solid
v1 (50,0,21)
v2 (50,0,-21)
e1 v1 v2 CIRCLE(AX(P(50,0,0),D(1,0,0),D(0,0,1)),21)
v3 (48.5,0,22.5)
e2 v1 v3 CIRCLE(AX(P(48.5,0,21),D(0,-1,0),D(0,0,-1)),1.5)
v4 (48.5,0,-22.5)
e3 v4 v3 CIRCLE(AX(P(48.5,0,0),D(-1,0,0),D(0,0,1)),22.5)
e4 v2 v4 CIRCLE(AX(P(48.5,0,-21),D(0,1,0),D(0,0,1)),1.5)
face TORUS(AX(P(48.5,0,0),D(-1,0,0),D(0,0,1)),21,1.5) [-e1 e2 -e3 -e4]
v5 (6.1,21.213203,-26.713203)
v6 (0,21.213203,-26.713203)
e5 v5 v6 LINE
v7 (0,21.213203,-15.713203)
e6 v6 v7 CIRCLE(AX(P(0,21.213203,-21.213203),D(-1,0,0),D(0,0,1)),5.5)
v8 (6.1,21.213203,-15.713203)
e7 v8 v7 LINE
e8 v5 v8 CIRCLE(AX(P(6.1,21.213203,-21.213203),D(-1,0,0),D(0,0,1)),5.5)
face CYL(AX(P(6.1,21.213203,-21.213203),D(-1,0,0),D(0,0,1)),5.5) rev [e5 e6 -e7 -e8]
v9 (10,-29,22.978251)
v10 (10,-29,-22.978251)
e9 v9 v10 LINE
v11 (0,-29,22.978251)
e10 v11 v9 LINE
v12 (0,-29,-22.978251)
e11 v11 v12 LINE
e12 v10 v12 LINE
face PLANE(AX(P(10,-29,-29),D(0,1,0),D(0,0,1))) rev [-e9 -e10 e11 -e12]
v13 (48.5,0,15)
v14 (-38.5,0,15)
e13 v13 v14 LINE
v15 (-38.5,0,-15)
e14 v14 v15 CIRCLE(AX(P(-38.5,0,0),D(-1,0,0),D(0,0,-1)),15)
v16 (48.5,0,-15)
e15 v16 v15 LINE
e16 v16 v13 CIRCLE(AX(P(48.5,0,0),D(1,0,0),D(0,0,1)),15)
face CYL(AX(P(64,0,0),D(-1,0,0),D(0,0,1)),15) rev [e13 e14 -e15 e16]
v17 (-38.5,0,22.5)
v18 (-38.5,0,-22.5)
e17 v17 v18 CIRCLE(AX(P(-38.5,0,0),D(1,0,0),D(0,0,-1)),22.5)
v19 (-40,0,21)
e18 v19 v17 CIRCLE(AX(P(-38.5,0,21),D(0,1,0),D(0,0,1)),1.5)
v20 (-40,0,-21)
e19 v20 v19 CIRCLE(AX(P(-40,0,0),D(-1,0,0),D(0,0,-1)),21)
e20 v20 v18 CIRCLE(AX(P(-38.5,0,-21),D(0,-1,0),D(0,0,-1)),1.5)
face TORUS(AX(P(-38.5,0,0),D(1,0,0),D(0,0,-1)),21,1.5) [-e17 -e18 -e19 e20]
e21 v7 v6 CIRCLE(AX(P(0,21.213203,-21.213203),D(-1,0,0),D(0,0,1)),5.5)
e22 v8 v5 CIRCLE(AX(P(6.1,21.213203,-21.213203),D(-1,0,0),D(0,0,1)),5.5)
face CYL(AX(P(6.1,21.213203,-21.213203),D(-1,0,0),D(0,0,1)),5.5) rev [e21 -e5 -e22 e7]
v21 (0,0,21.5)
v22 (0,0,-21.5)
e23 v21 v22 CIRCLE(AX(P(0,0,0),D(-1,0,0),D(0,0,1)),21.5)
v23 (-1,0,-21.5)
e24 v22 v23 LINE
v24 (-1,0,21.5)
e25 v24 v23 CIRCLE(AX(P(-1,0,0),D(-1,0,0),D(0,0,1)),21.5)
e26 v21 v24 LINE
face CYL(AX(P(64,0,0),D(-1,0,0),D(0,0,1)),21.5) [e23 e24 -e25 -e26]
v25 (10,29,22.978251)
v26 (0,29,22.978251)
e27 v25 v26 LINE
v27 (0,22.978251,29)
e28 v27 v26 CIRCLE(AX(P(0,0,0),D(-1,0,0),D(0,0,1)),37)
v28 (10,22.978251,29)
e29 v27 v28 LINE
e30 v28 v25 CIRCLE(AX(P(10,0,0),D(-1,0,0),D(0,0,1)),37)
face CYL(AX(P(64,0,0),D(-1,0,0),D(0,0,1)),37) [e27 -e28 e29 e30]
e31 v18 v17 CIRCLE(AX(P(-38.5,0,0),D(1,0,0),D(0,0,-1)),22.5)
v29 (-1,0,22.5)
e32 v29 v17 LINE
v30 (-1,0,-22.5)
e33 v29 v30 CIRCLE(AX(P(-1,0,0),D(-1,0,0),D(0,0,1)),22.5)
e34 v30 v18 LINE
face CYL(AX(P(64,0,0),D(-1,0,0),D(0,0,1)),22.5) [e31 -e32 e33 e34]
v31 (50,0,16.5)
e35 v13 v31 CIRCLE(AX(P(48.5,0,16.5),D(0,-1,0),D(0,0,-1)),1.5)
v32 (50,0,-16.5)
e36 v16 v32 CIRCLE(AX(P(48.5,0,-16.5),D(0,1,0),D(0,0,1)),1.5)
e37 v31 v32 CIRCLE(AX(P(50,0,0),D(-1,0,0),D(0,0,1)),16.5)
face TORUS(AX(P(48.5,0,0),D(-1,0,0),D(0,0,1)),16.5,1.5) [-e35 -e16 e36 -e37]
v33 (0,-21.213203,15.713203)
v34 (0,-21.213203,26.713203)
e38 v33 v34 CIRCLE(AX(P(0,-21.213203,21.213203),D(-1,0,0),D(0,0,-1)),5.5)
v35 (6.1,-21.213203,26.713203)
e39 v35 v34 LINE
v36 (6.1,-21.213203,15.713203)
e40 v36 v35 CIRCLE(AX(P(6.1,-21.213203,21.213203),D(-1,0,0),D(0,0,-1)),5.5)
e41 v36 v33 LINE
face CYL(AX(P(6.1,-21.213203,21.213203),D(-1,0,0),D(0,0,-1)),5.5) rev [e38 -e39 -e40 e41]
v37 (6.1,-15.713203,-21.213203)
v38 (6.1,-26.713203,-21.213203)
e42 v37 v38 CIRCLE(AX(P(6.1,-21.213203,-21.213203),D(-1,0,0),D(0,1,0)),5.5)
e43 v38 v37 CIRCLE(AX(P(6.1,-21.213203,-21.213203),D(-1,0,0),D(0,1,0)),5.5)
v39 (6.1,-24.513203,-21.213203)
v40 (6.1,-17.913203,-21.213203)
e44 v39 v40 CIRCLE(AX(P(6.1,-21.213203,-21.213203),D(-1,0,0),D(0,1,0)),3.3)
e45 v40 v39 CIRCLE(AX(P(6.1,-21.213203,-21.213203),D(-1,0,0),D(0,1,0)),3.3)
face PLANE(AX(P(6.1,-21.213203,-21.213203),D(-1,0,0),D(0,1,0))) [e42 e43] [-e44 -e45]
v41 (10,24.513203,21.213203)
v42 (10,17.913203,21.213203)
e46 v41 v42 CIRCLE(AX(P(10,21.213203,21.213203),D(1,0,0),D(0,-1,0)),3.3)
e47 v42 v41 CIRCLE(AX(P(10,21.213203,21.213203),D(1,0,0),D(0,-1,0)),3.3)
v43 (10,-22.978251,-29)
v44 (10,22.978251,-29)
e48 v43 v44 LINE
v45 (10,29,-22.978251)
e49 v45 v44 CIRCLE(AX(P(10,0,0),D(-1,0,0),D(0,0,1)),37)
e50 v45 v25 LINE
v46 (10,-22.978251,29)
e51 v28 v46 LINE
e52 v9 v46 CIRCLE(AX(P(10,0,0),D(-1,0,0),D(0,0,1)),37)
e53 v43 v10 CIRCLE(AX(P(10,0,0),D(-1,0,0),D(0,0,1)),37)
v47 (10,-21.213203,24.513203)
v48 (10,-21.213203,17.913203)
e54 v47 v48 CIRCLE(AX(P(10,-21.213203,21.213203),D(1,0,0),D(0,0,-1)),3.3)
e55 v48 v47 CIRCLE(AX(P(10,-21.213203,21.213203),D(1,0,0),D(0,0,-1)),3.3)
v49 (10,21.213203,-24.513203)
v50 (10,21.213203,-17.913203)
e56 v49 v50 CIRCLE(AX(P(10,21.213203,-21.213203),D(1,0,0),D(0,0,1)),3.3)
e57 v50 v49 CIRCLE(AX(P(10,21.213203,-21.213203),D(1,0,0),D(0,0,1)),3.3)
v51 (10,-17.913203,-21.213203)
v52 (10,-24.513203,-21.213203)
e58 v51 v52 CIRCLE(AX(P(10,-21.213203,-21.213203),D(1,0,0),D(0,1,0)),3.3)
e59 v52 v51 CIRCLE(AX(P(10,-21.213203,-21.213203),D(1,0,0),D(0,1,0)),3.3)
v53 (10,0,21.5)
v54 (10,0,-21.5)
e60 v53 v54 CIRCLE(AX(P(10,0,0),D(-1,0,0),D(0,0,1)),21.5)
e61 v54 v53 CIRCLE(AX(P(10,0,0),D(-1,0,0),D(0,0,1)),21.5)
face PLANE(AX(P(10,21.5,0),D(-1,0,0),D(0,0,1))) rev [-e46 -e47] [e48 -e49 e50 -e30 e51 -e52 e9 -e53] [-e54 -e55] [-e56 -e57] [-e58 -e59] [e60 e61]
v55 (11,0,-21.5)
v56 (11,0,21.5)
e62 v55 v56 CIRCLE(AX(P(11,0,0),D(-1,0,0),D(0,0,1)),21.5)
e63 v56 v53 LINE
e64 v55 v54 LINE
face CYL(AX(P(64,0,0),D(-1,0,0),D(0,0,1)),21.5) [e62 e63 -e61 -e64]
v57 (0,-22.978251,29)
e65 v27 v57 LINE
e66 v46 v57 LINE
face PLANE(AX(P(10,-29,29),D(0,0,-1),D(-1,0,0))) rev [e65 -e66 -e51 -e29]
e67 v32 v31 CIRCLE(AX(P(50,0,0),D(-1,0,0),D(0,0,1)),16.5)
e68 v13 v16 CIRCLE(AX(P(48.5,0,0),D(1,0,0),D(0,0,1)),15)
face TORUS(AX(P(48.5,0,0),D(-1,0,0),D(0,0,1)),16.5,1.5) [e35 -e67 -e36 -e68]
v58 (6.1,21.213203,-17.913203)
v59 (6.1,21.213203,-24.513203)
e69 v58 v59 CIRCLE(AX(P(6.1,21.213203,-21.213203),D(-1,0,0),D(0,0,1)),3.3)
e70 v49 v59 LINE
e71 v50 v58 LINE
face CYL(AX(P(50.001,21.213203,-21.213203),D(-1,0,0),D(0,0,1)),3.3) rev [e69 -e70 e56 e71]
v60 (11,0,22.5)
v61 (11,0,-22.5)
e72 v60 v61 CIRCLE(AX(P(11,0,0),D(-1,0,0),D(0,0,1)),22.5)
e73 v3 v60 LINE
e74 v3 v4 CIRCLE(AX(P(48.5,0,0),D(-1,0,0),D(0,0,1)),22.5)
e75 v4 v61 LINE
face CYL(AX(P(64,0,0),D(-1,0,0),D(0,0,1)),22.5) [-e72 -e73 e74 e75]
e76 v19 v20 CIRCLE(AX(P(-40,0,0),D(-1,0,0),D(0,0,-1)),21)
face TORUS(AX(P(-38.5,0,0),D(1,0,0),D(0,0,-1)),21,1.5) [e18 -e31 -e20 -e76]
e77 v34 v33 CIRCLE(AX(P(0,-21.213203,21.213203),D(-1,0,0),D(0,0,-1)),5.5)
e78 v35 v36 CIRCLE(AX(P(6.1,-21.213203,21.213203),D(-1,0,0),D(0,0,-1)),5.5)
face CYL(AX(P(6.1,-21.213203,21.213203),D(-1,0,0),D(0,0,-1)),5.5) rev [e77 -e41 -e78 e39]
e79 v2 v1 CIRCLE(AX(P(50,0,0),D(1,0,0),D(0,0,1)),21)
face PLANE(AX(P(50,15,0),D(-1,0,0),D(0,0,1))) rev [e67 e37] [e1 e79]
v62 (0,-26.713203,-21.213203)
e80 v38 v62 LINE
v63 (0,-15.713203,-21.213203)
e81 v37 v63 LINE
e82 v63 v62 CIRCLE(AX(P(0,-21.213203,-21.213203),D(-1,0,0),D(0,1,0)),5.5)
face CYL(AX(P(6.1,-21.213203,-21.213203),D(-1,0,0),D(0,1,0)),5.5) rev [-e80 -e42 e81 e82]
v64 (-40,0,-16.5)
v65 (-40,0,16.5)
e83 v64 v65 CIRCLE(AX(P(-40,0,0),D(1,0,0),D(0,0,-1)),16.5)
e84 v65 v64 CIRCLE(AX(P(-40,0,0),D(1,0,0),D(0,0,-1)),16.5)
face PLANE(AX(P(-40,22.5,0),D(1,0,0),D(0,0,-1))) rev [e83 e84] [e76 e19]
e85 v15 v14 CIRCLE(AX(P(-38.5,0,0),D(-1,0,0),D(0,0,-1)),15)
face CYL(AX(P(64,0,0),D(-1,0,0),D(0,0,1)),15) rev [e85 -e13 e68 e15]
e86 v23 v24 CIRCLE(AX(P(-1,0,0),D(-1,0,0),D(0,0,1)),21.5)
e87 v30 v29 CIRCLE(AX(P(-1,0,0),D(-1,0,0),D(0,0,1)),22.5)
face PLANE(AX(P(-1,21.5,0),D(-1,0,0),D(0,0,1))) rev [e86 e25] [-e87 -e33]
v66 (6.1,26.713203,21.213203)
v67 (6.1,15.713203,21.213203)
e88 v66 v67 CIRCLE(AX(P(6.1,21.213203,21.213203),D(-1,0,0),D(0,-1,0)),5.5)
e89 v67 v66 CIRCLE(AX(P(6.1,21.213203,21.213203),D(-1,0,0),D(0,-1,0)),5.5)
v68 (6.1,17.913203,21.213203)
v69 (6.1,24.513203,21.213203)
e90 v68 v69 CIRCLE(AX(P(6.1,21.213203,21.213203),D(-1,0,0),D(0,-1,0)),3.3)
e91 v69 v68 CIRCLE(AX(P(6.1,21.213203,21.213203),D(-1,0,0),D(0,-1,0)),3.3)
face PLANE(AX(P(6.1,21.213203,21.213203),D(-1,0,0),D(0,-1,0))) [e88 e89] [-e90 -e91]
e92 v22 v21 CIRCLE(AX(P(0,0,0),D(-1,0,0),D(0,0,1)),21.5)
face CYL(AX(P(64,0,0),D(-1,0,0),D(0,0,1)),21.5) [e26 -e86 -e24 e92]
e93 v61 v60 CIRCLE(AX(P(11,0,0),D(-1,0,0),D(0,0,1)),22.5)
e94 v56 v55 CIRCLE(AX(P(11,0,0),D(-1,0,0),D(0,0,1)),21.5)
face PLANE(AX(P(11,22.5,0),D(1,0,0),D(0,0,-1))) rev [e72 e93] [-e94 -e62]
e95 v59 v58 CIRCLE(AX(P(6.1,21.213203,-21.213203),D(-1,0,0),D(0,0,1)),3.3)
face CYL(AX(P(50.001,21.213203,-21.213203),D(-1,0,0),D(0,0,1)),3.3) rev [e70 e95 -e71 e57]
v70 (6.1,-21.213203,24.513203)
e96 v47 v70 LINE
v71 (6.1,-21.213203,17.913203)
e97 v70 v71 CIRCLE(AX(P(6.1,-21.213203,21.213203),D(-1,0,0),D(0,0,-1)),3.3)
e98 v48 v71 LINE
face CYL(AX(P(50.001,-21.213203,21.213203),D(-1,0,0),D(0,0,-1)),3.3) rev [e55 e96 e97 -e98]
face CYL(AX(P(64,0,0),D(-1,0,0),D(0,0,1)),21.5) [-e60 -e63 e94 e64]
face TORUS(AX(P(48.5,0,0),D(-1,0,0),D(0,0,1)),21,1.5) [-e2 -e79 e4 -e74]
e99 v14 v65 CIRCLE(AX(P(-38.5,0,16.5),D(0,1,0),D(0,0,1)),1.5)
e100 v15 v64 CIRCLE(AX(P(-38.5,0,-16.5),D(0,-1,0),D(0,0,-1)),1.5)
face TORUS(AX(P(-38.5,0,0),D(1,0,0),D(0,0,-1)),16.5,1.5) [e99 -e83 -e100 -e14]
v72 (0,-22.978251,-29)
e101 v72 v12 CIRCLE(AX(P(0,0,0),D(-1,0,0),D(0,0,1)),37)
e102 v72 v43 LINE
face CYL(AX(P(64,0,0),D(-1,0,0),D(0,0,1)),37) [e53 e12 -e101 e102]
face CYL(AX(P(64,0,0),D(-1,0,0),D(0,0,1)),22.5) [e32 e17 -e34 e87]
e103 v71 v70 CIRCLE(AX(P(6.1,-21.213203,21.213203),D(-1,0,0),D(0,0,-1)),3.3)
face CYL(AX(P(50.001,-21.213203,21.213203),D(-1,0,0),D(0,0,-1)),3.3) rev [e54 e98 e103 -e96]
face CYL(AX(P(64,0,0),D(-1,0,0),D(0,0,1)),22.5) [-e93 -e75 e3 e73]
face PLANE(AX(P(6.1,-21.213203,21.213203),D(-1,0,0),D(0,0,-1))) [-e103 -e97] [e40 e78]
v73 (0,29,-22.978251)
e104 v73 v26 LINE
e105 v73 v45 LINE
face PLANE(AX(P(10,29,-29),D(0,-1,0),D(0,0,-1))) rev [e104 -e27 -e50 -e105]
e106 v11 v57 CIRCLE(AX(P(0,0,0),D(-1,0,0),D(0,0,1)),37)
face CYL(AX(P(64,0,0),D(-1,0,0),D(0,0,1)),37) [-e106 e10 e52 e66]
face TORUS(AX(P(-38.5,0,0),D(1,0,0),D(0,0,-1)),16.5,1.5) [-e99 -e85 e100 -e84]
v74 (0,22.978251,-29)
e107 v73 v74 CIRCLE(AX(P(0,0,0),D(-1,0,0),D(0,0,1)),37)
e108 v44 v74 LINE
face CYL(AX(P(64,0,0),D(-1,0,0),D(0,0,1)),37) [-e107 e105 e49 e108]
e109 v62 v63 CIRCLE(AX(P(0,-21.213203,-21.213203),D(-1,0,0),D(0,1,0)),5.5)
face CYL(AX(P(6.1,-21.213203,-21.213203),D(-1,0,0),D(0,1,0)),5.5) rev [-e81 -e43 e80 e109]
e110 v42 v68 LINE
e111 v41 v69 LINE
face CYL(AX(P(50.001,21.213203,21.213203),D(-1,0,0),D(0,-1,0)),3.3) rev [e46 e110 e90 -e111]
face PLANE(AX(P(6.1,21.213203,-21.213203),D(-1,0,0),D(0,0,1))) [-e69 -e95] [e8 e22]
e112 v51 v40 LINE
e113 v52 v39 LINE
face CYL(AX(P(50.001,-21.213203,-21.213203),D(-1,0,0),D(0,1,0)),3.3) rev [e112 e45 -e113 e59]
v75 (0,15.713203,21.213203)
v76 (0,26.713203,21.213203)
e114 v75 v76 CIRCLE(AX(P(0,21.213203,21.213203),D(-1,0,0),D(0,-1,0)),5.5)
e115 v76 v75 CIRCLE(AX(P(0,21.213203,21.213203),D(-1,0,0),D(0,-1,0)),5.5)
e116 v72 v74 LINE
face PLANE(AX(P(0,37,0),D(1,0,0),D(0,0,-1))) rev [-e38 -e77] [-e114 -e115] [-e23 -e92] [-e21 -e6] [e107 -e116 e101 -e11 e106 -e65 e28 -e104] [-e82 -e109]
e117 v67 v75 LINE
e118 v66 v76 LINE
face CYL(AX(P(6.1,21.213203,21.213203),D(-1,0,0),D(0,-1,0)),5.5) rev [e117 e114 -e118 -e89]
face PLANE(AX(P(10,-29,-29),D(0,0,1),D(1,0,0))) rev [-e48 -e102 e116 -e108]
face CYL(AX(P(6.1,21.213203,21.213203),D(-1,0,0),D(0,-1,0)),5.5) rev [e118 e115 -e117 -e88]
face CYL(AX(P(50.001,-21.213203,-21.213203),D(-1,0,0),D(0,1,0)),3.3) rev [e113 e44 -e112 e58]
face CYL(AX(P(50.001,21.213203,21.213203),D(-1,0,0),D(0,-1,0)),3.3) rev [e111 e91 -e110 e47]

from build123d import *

# Parameters (mm, degrees)
SKETCH2_OUTSIDE_W   = 103.606
SKETCH2_OUTSIDE_H   = 103.606
SKETCH2_OUTSIDE_W_2 = 58
SKETCH2_OUTSIDE_H_2 = 58
CUT_EXTRUDE1_DEPTH  = 10
SKETCH3_R           = 5.5
CUT_EXTRUDE2_DEPTH  = 6.1
CUT_EXTRUDE3_REACH  = 63.703
SKETCH4_R           = 3.3
CIRPATTERN1_COUNT   = 4
FILLET1_R           = 1.5


with BuildPart() as part:
    # Sketch1 → Revolve1 (revolve)
    with BuildSketch(Plane.XY, mode=Mode.PRIVATE) as revolve1_sk:
        Polygon((0, 37), (0, 21.5), (-1, 21.5), (-1, 22.5), (-40, 22.5), (-40, 15), (0, 15), (50, 15), (50, 22.5), (11, 22.5), (11, 21.5), (10, 21.5), (10, 37), align=None)
    revolve(revolve1_sk.sketch.rotate(Axis((64, 0, 0), (-1, 0, 0)), 270), axis=Axis((64, 0, 0), (-1, 0, 0)))

    # Sketch2 outside → Cut-Extrude1 (cut)
    with BuildSketch(Plane(origin=(0, 0, 0), x_dir=(0, 0, -1), z_dir=(1, 0, 0))):
        Rectangle(SKETCH2_OUTSIDE_W, SKETCH2_OUTSIDE_H)
        Rectangle(SKETCH2_OUTSIDE_W_2, SKETCH2_OUTSIDE_H_2, mode=Mode.SUBTRACT)
    extrude(amount=CUT_EXTRUDE1_DEPTH, mode=Mode.SUBTRACT)

    # Sketch3 → Cut-Extrude2 (cut)
    with BuildSketch(Plane.ZY):
        with Locations((-21.213203436, 21.213203436)):
            Circle(SKETCH3_R)
    cut_extrude2 = extrude(amount=-CUT_EXTRUDE2_DEPTH, mode=Mode.SUBTRACT)

    # Sketch4 → Cut-Extrude3 (cut, up to next)
    with BuildSketch(Plane.ZY.offset(-6.1), mode=Mode.PRIVATE) as cut_extrude3_sk1:
        with Locations((-21.213203436, 21.213203436)):
            Circle(SKETCH4_R)
    cut_extrude3_tool1 = extrude(cut_extrude3_sk1.sketch, amount=-CUT_EXTRUDE3_REACH, mode=Mode.PRIVATE) & part.part
    cut_extrude3 = cut_extrude3_tool1.solids().sort_by_distance((6.1, 21.213203, -21.213203))[0]
    add(cut_extrude3, mode=Mode.SUBTRACT)

    # CirPattern1: Cut-Extrude2, Cut-Extrude3 ×4 about axis
    cirpattern1_axis = Axis((0, 0, 0), (1, 0, 0))
    add([cut_extrude2.rotate(cirpattern1_axis, i * 360 / CIRPATTERN1_COUNT) for i in range(1, CIRPATTERN1_COUNT)], mode=Mode.SUBTRACT)
    add([cut_extrude3.rotate(cirpattern1_axis, i * 360 / CIRPATTERN1_COUNT) for i in range(1, CIRPATTERN1_COUNT)], mode=Mode.SUBTRACT)

    # Fillet1
    fillet1_edges = [part.edges().sort_by_distance(p)[0] for p in [
        (50, 0, -22.5),
        (50, 0, -15),
        (-40, 0, -15),
        (-40, 0, -22.5),
    ]]
    fillet(fillet1_edges, radius=FILLET1_R)


solid = part.part
